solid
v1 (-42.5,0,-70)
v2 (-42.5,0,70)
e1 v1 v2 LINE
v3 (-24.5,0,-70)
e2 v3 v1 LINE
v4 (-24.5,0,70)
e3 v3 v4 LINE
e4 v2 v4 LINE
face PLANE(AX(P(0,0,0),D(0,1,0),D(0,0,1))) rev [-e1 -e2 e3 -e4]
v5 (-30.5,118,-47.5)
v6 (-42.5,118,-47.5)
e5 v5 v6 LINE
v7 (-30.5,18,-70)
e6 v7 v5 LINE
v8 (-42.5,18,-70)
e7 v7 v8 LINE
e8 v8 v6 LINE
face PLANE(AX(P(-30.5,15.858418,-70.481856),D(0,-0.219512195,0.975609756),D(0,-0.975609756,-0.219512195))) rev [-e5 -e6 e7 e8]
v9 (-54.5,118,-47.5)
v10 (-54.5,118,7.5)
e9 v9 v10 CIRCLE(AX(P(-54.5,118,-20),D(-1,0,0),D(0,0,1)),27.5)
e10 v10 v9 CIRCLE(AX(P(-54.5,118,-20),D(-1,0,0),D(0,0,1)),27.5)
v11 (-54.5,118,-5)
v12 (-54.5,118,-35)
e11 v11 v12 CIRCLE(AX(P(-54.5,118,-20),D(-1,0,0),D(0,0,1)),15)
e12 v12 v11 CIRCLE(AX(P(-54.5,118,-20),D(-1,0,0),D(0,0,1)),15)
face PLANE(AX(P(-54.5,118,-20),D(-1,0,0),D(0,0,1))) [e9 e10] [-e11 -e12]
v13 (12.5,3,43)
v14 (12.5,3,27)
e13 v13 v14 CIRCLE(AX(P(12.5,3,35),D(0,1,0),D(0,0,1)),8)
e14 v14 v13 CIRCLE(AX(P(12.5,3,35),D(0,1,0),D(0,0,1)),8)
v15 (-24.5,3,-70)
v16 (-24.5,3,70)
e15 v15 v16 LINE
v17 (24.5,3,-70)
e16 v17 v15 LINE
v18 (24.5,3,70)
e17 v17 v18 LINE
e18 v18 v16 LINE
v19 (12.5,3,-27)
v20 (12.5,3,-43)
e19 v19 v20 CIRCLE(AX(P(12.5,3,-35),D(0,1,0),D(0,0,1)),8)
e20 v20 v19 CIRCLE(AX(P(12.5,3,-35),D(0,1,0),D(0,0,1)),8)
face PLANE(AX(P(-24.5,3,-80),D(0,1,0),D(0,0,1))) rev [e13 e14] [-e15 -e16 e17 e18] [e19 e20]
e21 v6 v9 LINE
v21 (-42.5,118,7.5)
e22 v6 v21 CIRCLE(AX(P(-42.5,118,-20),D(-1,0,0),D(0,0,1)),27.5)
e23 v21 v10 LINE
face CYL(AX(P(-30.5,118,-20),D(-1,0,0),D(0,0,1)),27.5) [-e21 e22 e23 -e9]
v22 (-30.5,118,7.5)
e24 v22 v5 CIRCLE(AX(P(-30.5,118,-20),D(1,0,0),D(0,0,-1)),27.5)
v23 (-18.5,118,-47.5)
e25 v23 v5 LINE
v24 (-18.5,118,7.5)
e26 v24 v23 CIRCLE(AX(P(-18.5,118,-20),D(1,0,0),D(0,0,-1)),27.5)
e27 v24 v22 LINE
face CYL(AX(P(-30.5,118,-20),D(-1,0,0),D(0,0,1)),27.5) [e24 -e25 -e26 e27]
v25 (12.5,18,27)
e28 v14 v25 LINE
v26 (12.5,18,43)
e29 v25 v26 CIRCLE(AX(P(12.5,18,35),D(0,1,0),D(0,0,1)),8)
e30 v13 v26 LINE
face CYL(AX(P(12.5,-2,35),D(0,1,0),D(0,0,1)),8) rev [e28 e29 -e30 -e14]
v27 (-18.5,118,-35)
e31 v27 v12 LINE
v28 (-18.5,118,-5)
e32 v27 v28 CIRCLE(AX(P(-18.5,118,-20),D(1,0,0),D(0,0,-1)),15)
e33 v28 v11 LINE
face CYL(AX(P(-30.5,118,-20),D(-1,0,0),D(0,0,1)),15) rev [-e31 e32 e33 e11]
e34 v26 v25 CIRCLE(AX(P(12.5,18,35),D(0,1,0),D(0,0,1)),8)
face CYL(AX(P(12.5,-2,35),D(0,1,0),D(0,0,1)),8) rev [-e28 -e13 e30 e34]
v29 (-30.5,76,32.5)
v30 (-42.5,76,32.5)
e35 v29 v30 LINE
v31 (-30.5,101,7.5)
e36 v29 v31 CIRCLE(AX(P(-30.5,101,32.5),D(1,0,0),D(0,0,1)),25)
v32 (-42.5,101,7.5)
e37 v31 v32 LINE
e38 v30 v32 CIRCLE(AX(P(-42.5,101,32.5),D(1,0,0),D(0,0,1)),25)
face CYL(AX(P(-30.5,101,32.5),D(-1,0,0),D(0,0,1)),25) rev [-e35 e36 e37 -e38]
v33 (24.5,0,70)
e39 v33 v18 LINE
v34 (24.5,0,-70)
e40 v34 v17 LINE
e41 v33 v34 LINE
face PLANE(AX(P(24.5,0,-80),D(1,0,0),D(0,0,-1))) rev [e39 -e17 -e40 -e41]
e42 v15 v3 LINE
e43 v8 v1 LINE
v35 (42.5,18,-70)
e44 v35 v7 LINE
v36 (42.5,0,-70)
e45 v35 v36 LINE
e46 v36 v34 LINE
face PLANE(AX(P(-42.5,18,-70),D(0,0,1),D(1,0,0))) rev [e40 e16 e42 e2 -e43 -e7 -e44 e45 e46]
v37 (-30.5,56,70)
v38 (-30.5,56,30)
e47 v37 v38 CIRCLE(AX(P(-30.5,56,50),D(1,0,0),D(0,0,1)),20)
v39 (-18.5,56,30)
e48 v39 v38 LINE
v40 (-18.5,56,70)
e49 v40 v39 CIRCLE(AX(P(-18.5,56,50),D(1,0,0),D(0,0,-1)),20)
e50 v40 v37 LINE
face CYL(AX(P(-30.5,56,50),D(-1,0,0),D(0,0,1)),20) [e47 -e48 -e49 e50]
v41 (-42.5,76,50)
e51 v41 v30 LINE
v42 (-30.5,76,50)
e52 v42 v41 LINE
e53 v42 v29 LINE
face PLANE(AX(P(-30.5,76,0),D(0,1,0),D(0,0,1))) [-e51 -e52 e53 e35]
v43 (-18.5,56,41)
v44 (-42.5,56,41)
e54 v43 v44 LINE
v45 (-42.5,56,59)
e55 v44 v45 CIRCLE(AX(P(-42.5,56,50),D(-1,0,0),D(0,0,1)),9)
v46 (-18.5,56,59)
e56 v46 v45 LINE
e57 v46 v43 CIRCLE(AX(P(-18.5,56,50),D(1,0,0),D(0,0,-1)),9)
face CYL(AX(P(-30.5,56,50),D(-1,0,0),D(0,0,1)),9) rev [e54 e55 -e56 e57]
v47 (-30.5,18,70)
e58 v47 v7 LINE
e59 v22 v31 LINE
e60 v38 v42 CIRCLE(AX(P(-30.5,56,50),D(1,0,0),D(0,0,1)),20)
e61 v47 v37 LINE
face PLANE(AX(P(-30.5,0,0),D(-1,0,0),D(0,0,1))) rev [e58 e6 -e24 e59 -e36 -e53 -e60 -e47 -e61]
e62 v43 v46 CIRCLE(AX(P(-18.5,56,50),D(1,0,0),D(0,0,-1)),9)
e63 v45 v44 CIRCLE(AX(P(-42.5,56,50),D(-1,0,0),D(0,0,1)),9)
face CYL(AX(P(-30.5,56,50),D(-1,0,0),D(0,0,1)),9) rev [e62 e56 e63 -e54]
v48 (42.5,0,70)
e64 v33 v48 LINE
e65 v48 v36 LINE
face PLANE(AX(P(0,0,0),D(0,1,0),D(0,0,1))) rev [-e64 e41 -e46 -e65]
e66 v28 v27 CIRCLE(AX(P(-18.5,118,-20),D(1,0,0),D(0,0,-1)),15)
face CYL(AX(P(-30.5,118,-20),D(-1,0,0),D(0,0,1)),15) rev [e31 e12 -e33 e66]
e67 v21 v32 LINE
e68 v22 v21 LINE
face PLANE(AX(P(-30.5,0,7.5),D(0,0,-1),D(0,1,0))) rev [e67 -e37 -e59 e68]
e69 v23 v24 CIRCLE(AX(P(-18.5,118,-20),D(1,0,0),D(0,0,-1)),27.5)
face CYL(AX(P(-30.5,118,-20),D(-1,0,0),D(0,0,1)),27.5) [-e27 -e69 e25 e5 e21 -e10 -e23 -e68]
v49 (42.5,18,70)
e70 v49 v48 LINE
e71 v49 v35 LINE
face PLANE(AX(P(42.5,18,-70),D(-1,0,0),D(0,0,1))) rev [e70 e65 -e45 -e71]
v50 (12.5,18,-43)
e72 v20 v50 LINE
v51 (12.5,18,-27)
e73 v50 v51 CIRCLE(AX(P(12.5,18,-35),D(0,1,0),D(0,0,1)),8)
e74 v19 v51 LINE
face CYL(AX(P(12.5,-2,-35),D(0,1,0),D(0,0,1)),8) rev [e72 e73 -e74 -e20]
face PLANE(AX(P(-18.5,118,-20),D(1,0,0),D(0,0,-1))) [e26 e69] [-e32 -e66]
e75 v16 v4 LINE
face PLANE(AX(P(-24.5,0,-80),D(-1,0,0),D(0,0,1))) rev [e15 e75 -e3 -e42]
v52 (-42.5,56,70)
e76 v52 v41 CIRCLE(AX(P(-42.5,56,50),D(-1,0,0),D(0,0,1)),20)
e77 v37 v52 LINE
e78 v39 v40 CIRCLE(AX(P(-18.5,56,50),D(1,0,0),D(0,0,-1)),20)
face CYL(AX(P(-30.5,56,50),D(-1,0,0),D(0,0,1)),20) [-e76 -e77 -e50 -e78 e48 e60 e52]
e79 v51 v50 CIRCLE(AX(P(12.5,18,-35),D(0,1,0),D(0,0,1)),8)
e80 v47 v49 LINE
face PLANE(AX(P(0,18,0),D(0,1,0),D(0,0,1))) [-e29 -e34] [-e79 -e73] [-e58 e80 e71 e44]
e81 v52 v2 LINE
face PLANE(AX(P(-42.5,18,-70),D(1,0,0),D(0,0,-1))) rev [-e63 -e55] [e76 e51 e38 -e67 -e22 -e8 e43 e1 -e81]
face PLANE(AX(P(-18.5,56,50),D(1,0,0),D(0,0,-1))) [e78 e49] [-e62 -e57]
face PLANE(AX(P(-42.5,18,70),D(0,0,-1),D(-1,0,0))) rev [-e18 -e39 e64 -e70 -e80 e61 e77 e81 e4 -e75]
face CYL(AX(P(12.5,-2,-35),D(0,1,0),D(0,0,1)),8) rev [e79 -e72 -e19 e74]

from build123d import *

# Parameters (mm, degrees)
BASE_PLATE_SKETCH_W              = 85
BASE_PLATE_SKETCH_H              = 140
BASE_PLATE_140X85X18_DEPTH       = 18
UNDERSIDE_RELIEF_GROOVE_SKETCH_W = 49
UNDERSIDE_RELIEF_GROOVE_SKETCH_H = 3
UNDERSIDE_RELIEF_GROOVE_DEPTH    = 150
ANGLED_SUPPORT_WEB_SKETCH_R      = 20
ANGLED_SUPPORT_WEB_SKETCH_R_2    = 9
ANGLED_SUPPORT_WEB_SKETCH_R_3    = 27.5
ANGLED_SUPPORT_WEB_SKETCH_R_4    = 15
ANGLED_SUPPORT_WEB_DEPTH         = 12
UPPER_BOSS_SKETCH_R              = 20
UPPER_BOSS_SKETCH_R_2            = 9
UPPER_BOSS_40_DEPTH              = 12
LOWER_START                      = 12
LOWER_BOSS_SKETCH_A_R            = 27.5
LOWER_BOSS_SKETCH_A_R_2          = 15
LOWER_BOSS_30_A_DEPTH            = 12
LOWER_BOSS_SKETCH_B_R            = 27.5
LOWER_BOSS_SKETCH_B_R_2          = 15
LOWER_BOSS_30_B_DEPTH            = 12
BASE_MOUNTING_HOLES_SKETCH_R     = 8
BASE_MOUNTING_HOLES_2X_16_DEPTH  = 20


with BuildPart() as part:
    # Base Plate Sketch → Base Plate 140x85x18 (new body)
    with BuildSketch(Plane(origin=(0, 0, 0), x_dir=(1, 0, 0), z_dir=(0, 1, 0))):
        Rectangle(BASE_PLATE_SKETCH_W, BASE_PLATE_SKETCH_H)
    extrude(amount=BASE_PLATE_140X85X18_DEPTH)

    # Underside Relief Groove Sketch → Underside Relief Groove (cut)
    with BuildSketch(Plane.XY.offset(70)):
        with Locations((0, 1.5)):
            Rectangle(UNDERSIDE_RELIEF_GROOVE_SKETCH_W, UNDERSIDE_RELIEF_GROOVE_SKETCH_H)
    extrude(amount=-UNDERSIDE_RELIEF_GROOVE_DEPTH, mode=Mode.SUBTRACT)

    # Angled Support Web Sketch → Angled Support Web (add)
    # profile 1 of 3: a face of its own
    with BuildSketch(Plane.ZY.offset(42.5)):
        with BuildLine():
            Line((-70, 18), (70, 18))
            Line((70, 18), (70, 56))
            ThreePointArc((70, 56), (35.857864376, 41.857864376), (50, 76))
            Line((50, 76), (32.5, 76))
            ThreePointArc((32.5, 76), (14.82233047, 83.32233047), (7.5, 101))
            Line((7.5, 101), (7.5, 118))
            ThreePointArc((7.5, 118), (-20, 90.5), (-47.5, 118))
            Line((-47.5, 118), (-70, 18))
        make_face()
    # profile 2 of 3: a face of its own
    with BuildSketch(Plane.ZY.offset(42.5)):
        with Locations((50, 56)):
            Circle(ANGLED_SUPPORT_WEB_SKETCH_R)
        with Locations((50, 56)):
            Circle(ANGLED_SUPPORT_WEB_SKETCH_R_2, mode=Mode.SUBTRACT)
    # profile 3 of 3: a face of its own
    with BuildSketch(Plane.ZY.offset(42.5)):
        with Locations((-20, 118)):
            Circle(ANGLED_SUPPORT_WEB_SKETCH_R_3)
        with Locations((-20, 118)):
            Circle(ANGLED_SUPPORT_WEB_SKETCH_R_4, mode=Mode.SUBTRACT)
    extrude(amount=-ANGLED_SUPPORT_WEB_DEPTH)

    # Upper Boss Sketch → Upper Boss Ø40 (add)
    with BuildSketch(Plane(origin=(-30.5, 0, 0), x_dir=(0, 0, -1), z_dir=(1, 0, 0))):
        with Locations(Location((-50, 56, 0), (0, 0, 180))):
            Circle(UPPER_BOSS_SKETCH_R)
        with Locations(Location((-50, 56, 0), (0, 0, 180))):
            Circle(UPPER_BOSS_SKETCH_R_2, mode=Mode.SUBTRACT)
    extrude(amount=UPPER_BOSS_40_DEPTH)

    # Lower Boss Sketch A → Lower Boss Ø30 A (add)
    with BuildSketch(Plane.ZY.offset(42.5).offset(LOWER_START)):
        with Locations((-20, 118)):
            Circle(LOWER_BOSS_SKETCH_A_R)
        with Locations((-20, 118)):
            Circle(LOWER_BOSS_SKETCH_A_R_2, mode=Mode.SUBTRACT)
    extrude(amount=-LOWER_BOSS_30_A_DEPTH)

    # Lower Boss Sketch B → Lower Boss Ø30 B (add)
    with BuildSketch(Plane(origin=(-30.5, 0, 0), x_dir=(0, 0, -1), z_dir=(1, 0, 0))):
        with Locations(Location((20, 118, 0), (0, 0, 180))):
            Circle(LOWER_BOSS_SKETCH_B_R)
        with Locations(Location((20, 118, 0), (0, 0, 180))):
            Circle(LOWER_BOSS_SKETCH_B_R_2, mode=Mode.SUBTRACT)
    extrude(amount=LOWER_BOSS_30_B_DEPTH)

    # Base Mounting Holes Sketch → Base Mounting Holes 2xØ16 (cut)
    with BuildSketch(Plane(origin=(0, 18, 0), x_dir=(1, 0, 0), z_dir=(0, 1, 0))):
        with Locations(Location((12.5, 35, 0), (0, 0, 270))):
            Circle(BASE_MOUNTING_HOLES_SKETCH_R)
        with Locations(Location((12.5, -35, 0), (0, 0, 270))):
            Circle(BASE_MOUNTING_HOLES_SKETCH_R)
    extrude(amount=-BASE_MOUNTING_HOLES_2X_16_DEPTH, mode=Mode.SUBTRACT)


solid = part.part
